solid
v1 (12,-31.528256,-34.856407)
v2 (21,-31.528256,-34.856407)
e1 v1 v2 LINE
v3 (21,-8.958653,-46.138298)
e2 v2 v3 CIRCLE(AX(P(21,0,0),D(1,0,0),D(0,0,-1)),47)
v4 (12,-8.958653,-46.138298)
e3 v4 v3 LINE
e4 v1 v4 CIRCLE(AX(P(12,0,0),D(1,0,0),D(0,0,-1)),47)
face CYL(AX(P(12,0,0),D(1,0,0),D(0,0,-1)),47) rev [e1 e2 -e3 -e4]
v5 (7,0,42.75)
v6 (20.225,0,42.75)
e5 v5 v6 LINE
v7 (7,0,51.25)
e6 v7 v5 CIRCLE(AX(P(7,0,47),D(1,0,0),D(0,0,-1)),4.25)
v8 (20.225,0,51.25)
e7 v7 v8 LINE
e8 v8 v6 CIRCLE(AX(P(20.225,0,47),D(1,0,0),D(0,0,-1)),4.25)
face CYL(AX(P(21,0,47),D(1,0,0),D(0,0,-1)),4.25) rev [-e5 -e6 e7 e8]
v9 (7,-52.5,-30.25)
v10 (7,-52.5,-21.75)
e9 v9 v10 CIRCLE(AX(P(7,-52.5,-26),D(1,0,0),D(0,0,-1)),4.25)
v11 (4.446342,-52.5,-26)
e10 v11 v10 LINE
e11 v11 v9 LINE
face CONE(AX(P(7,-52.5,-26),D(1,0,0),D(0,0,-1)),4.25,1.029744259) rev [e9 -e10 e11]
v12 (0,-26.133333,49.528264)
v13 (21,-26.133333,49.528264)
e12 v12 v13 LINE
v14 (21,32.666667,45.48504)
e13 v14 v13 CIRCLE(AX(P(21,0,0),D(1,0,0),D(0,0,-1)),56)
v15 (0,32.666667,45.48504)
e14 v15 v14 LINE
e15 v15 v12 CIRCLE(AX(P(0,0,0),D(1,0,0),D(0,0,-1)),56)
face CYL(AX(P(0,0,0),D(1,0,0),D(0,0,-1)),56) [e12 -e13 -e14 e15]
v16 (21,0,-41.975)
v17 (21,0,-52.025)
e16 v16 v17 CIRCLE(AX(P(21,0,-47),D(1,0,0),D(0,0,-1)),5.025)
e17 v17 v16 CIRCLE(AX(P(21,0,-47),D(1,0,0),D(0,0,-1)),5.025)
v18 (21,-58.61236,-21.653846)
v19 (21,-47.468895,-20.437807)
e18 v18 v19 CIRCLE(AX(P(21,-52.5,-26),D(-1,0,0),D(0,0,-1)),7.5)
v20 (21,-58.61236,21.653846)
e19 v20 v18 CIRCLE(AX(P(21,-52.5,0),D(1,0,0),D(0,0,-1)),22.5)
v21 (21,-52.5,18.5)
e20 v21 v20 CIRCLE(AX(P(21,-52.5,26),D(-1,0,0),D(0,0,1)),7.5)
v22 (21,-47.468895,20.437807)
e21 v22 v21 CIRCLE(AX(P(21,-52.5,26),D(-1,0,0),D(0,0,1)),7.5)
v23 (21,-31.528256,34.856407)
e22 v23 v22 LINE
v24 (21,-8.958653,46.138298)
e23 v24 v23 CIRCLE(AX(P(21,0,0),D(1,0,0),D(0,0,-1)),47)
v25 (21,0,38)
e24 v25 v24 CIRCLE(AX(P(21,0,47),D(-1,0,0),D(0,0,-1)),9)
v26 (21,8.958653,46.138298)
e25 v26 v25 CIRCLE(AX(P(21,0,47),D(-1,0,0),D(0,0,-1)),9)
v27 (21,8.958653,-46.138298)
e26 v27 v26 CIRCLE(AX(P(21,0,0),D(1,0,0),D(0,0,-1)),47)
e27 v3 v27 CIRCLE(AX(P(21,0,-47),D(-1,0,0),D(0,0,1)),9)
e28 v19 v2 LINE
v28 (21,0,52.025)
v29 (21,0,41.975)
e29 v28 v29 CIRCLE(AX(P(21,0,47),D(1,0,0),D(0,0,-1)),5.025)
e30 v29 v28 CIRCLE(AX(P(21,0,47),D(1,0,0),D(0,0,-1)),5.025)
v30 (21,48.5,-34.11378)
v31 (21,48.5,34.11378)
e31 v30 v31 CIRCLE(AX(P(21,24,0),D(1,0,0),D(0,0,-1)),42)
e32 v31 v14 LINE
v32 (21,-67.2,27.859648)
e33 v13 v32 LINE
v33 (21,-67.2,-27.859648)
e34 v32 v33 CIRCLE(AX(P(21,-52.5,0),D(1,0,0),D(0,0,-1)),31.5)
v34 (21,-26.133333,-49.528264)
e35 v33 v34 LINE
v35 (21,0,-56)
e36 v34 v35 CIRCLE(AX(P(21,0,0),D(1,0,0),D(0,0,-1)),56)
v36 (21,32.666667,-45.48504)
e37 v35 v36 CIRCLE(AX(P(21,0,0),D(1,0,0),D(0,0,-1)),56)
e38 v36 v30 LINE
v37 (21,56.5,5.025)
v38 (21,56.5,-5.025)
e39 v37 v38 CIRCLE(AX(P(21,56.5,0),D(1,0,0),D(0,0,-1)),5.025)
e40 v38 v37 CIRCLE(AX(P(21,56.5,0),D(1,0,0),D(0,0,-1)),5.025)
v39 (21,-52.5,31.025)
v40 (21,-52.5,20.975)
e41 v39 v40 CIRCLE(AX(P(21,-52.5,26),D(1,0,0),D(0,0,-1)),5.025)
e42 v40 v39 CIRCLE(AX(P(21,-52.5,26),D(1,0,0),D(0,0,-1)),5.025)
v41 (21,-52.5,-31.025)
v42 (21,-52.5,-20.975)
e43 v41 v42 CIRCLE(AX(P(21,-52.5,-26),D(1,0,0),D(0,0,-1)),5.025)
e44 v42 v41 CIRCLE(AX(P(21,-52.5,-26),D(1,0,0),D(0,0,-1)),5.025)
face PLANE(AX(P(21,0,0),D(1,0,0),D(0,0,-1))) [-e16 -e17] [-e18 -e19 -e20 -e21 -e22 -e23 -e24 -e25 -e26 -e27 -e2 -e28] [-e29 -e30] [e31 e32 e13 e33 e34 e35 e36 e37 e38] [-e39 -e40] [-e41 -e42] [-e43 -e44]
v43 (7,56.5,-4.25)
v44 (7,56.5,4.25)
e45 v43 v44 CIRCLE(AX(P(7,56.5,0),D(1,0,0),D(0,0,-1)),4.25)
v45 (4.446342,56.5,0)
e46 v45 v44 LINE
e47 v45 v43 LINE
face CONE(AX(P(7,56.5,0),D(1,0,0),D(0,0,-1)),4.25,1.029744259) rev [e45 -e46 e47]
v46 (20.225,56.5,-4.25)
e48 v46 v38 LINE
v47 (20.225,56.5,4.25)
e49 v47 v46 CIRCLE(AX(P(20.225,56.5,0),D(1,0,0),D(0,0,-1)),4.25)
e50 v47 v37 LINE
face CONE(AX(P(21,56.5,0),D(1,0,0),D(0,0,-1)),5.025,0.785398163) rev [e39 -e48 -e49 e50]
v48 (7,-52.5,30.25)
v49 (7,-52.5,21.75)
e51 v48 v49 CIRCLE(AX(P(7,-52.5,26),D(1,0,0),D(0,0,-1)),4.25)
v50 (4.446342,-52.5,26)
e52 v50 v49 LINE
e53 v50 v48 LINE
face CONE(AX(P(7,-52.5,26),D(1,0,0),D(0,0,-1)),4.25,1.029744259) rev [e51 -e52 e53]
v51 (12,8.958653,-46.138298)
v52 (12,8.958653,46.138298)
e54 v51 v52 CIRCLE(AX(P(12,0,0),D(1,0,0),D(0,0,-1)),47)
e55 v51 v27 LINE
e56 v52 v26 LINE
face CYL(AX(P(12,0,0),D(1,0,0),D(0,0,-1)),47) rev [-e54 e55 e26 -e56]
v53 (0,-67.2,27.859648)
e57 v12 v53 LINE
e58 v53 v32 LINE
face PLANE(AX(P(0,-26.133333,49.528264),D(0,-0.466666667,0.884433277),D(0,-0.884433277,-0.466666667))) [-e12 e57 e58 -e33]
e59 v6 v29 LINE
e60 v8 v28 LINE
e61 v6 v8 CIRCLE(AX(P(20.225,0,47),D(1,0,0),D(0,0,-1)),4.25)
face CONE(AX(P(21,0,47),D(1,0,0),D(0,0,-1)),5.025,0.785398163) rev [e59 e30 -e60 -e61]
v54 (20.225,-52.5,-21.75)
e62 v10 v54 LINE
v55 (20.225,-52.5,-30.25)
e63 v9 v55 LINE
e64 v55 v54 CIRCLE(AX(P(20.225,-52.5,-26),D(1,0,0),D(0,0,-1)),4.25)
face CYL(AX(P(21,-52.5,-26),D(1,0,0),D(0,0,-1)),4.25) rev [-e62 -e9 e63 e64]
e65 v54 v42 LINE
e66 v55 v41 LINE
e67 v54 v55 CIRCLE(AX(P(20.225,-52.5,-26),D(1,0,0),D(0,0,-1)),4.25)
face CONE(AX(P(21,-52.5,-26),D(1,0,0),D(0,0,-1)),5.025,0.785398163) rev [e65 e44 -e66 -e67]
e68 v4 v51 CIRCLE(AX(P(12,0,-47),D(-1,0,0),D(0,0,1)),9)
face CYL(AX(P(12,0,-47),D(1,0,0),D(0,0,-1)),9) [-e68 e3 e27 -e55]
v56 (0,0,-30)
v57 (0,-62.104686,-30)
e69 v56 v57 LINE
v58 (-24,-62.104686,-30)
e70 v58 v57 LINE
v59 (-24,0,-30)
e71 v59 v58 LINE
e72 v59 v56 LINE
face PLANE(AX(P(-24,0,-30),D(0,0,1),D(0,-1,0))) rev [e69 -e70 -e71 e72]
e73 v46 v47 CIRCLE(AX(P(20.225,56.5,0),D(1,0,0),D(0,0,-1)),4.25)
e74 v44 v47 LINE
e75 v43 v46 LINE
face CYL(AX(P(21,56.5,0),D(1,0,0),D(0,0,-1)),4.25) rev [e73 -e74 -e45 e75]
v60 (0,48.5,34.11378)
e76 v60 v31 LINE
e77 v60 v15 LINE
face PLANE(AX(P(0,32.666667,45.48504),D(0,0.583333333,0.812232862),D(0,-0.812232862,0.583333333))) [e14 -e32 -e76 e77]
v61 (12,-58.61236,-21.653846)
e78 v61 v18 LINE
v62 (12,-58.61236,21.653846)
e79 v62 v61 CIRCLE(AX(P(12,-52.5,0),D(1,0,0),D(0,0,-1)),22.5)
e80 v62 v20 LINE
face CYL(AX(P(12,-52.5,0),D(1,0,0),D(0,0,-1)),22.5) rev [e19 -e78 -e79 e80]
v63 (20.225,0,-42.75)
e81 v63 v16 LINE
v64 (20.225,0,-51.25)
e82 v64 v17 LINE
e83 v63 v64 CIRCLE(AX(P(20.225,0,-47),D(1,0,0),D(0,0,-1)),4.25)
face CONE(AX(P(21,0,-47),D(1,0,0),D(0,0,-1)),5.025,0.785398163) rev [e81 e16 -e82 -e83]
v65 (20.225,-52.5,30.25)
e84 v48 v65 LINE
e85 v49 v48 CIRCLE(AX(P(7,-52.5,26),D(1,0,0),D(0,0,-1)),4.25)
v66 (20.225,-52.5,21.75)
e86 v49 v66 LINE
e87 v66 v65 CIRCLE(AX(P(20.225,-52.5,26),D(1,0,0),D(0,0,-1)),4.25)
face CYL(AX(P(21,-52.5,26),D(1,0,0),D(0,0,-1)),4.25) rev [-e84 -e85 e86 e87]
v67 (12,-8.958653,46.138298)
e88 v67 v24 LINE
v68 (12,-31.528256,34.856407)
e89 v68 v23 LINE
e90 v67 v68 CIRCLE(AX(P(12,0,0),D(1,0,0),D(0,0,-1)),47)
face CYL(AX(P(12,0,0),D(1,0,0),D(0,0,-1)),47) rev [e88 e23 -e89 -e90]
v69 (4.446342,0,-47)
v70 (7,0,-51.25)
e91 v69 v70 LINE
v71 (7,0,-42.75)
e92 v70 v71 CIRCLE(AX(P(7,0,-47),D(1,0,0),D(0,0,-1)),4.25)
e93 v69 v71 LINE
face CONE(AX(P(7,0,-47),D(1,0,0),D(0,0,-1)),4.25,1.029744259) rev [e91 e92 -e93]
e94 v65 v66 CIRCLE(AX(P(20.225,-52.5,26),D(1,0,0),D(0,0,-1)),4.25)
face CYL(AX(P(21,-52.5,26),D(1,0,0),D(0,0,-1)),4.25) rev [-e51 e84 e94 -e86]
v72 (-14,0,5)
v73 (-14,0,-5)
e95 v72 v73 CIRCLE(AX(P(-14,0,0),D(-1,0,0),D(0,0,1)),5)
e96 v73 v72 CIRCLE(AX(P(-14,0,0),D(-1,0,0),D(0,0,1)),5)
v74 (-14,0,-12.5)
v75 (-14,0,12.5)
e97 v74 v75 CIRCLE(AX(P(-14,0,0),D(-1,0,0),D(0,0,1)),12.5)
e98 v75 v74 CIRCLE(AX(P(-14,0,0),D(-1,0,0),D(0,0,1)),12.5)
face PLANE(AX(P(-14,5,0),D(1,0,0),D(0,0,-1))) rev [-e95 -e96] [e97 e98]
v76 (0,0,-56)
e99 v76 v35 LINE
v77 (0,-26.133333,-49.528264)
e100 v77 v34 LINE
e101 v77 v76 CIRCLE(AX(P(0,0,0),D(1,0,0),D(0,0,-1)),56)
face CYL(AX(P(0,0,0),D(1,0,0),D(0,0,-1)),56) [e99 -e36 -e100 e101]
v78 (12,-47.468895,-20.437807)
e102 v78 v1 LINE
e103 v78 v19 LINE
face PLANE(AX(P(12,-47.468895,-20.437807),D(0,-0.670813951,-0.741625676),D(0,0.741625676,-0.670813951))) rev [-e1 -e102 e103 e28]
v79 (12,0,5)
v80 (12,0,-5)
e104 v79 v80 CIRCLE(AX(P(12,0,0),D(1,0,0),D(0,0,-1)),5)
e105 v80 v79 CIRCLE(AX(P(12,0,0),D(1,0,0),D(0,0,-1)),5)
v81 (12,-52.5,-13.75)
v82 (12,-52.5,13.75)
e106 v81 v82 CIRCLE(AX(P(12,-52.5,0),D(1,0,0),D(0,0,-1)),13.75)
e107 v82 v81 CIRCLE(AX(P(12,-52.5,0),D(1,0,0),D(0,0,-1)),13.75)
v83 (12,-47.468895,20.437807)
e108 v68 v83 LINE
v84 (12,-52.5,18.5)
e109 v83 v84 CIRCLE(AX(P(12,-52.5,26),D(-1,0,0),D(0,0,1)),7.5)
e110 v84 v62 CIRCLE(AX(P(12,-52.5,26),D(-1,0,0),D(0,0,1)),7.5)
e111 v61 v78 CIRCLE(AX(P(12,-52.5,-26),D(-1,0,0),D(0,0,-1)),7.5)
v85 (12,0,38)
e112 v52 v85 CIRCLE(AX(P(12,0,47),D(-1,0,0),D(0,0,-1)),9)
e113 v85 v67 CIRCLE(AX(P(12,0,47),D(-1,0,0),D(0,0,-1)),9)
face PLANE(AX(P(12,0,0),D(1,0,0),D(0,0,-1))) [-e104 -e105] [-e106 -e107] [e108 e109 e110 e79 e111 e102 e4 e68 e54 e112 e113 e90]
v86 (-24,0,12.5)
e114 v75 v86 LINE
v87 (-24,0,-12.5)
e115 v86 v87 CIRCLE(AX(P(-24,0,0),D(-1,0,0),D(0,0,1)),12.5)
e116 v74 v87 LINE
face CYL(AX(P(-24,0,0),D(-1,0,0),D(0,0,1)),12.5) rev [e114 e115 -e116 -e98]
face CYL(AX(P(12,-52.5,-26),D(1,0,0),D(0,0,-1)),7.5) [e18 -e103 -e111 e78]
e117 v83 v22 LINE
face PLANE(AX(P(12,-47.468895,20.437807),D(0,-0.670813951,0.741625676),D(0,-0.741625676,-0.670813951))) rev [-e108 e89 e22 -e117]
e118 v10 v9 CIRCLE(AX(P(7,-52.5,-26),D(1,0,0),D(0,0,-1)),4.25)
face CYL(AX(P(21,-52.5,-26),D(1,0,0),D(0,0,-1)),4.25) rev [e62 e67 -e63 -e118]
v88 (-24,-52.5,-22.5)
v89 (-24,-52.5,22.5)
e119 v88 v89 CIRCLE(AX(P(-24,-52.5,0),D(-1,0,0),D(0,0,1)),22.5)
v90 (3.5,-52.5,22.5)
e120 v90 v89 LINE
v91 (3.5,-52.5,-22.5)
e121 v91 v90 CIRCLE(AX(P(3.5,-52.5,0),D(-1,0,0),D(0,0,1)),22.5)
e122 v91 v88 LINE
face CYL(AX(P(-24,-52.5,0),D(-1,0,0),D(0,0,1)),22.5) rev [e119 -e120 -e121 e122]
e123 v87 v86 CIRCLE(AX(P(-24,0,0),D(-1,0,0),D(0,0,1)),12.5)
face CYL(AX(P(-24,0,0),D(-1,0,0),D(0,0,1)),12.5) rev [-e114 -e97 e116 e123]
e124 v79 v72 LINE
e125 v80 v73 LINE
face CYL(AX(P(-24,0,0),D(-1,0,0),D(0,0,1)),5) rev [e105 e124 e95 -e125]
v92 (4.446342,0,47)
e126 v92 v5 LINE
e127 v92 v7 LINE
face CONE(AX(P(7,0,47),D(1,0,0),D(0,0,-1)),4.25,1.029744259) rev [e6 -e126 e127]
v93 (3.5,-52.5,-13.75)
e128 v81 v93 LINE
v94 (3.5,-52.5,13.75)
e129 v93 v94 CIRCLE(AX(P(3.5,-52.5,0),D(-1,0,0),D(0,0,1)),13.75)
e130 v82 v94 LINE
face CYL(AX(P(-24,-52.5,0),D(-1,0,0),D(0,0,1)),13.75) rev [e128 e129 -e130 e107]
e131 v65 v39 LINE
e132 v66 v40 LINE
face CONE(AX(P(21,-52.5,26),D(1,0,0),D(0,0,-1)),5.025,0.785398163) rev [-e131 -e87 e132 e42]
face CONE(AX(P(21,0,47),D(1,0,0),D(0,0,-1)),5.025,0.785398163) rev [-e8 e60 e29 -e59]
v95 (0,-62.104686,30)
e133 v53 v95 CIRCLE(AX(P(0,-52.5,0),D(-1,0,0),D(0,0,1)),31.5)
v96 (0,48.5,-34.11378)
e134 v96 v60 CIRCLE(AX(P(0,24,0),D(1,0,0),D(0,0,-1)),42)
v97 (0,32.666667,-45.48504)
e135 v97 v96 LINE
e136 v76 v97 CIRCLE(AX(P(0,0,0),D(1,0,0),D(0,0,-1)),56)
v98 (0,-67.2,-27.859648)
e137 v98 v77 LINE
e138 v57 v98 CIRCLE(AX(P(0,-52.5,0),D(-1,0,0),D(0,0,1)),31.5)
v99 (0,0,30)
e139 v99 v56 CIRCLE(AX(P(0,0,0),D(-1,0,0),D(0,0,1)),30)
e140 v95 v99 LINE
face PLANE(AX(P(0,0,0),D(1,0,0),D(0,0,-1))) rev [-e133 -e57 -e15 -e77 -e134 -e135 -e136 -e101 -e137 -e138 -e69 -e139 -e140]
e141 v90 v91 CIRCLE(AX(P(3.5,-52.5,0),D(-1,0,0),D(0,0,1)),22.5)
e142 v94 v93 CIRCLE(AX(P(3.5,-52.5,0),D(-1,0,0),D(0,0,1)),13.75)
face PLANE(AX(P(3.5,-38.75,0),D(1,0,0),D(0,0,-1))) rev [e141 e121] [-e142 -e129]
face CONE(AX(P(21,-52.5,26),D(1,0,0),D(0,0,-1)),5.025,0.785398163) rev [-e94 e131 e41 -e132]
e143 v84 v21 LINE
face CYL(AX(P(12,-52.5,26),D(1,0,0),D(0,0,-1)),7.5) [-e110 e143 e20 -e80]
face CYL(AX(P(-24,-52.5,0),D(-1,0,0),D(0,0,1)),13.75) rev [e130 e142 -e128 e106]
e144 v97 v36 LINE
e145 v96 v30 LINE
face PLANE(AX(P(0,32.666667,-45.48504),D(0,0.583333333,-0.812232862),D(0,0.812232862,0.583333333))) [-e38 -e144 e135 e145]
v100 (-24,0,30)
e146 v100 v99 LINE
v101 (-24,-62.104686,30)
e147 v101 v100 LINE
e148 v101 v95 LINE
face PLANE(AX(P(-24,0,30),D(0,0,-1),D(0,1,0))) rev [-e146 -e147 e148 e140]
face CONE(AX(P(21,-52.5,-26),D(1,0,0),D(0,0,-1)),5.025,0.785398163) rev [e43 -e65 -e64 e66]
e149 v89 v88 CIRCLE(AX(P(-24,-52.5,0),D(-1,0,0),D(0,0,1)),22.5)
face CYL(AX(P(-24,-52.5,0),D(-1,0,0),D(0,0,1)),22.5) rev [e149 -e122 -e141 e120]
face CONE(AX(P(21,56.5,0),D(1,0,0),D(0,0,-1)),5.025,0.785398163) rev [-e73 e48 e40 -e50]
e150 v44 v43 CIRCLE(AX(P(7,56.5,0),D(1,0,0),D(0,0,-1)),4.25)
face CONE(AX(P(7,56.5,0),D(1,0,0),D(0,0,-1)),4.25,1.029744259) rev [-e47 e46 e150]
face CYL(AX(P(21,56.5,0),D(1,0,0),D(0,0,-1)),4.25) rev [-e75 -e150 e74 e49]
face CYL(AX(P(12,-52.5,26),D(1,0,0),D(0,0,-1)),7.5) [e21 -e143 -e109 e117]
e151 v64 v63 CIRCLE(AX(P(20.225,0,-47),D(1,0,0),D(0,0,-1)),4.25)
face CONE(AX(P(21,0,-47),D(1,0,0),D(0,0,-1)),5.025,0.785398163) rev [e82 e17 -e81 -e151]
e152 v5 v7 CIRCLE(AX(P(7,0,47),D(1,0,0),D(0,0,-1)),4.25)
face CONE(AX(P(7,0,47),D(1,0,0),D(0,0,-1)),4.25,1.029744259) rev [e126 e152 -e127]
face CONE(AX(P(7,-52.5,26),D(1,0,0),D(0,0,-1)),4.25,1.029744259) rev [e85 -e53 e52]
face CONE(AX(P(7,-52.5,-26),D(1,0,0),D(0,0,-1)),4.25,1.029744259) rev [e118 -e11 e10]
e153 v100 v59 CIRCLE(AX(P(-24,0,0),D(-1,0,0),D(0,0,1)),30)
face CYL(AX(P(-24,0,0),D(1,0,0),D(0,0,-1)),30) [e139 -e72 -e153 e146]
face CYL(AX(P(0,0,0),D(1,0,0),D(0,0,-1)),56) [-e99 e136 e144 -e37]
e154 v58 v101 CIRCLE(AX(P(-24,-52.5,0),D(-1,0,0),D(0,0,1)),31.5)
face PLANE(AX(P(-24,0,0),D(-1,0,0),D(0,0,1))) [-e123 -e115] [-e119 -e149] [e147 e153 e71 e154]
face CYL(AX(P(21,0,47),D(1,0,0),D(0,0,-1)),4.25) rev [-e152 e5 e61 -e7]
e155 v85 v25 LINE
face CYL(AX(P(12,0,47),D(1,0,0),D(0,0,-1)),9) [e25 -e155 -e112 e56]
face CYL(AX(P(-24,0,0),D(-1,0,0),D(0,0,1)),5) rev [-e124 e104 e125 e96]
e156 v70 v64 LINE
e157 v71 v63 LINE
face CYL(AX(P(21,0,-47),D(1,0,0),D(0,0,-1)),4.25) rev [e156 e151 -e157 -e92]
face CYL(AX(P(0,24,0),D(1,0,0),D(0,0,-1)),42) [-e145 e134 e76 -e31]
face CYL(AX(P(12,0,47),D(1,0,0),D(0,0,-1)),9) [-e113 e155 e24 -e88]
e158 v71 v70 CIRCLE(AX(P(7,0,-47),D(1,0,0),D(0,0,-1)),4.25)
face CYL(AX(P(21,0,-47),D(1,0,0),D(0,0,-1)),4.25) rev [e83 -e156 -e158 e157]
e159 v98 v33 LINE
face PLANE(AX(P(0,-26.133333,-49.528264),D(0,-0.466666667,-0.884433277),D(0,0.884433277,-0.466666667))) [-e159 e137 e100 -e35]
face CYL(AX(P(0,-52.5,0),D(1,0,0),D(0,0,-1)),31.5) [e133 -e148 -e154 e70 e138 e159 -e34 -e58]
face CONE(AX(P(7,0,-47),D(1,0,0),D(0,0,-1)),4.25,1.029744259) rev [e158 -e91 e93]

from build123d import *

# Parameters (mm, degrees)
PLATE_PROFILE_SKETCH_W             = 112
PLATE_PROFILE_SKETCH_H             = 150
COVER_PLATE_21MM_DEPTH             = 21
INNER_RECESS_SKETCH_OUTSIDE_W      = 151.674
INNER_RECESS_SKETCH_OUTSIDE_H      = 189.674
INNER_RECESS_CUT_DEPTH             = 21
BORE_BOSS_60_DEPTH                 = 24
FACE_RECESS_9MM_DEPTH              = 9
M10_TAPPED_HOLES_D                 = 8.5
M10_TAPPED_HOLES_DEPTH             = 14
M10_TAPPED_HOLES_CSINK_D           = 10.05
M10_TAPPED_HOLES_CSINK_ANGLE       = 90
M10_TAPPED_HOLES_TIP               = 2.553657631
COUNTERBORED_HOLE_10_D             = 10
COUNTERBORED_HOLE_10_DEPTH         = 100
COUNTERBORED_HOLE_10_CBORE_D       = 25
COUNTERBORED_HOLE_10_CBORE_DEPTH   = 10
COUNTERBORED_BORE_27_5_D           = 27.5
COUNTERBORED_BORE_27_5_DEPTH       = 100
COUNTERBORED_BORE_27_5_CBORE_D     = 45
COUNTERBORED_BORE_27_5_CBORE_DEPTH = 27.5


with BuildPart() as part:
    # Plate Profile Sketch → Cover Plate 21mm (new body)
    with BuildSketch(Plane(origin=(0, 0, 0), x_dir=(0, 0, -1), z_dir=(1, 0, 0))):
        with Locations((0, -9)):
            Rectangle(PLATE_PROFILE_SKETCH_W, PLATE_PROFILE_SKETCH_H)
    extrude(amount=COVER_PLATE_21MM_DEPTH)

    # Inner Recess Sketch outside → Inner Recess Cut (cut)
    with BuildSketch(Plane(origin=(21, 0, 0), x_dir=(0, 0, -1), z_dir=(1, 0, 0))):
        with Locations((0, -9)):
            Rectangle(INNER_RECESS_SKETCH_OUTSIDE_W, INNER_RECESS_SKETCH_OUTSIDE_H)
        with BuildLine():
            Line((-49.528263536, -26.133333333), (-27.859648239, -67.2))
            ThreePointArc((-27.859648239, -67.2), (0, -84), (27.859648239, -67.2))
            Line((27.859648239, -67.2), (49.528263536, -26.133333333))
            ThreePointArc((49.528263536, -26.133333333), (55.868076531, 3.841617458), (45.485040276, 32.666666667))
            Line((45.485040276, 32.666666667), (34.113780207, 48.5))
            ThreePointArc((34.113780207, 48.5), (0, 66), (-34.113780207, 48.5))
            Line((-34.113780207, 48.5), (-45.485040276, 32.666666667))
            ThreePointArc((-45.485040276, 32.666666667), (-55.868076531, 3.841617458), (-49.528263536, -26.133333333))
        make_face(mode=Mode.SUBTRACT)
    extrude(amount=-INNER_RECESS_CUT_DEPTH, mode=Mode.SUBTRACT)

    # Bore Boss Sketch → Bore Boss Ø60 (add)
    with BuildSketch(Plane.ZY):
        with BuildLine():
            Line((30, 0), (30, -62.104686356))
            ThreePointArc((30, -62.104686356), (0, -84), (-30, -62.104686356))
            Line((-30, -62.104686356), (-30, 0))
            ThreePointArc((-30, 0), (0, 30), (30, 0))
        make_face()
    extrude(amount=BORE_BOSS_60_DEPTH)

    # Face Recess Sketch → Face Recess 9mm (cut)
    with BuildSketch(Plane(origin=(21, 0, 0), x_dir=(0, 0, -1), z_dir=(1, 0, 0))):
        with BuildLine():
            Line((-20.437807431, -47.468895368), (-34.856406768, -31.528255696))
            ThreePointArc((-34.856406768, -31.528255696), (-42.040245988, -21.014702408), (-46.138297872, -8.958653328))
            ThreePointArc((-46.138297872, -8.958653328), (-38, 0), (-46.138297872, 8.958653328))
            ThreePointArc((-46.138297872, 8.958653328), (0, 47), (46.138297872, 8.958653328))
            ThreePointArc((46.138297872, 8.958653328), (38, 0), (46.138297872, -8.958653328))
            ThreePointArc((46.138297872, -8.958653328), (42.040245988, -21.014702408), (34.856406768, -31.528255696))
            Line((34.856406768, -31.528255696), (20.437807431, -47.468895368))
            ThreePointArc((20.437807431, -47.468895368), (18.544261668, -53.313612883), (21.653846154, -58.612360162))
            ThreePointArc((21.653846154, -58.612360162), (0, -75), (-21.653846154, -58.612360162))
            ThreePointArc((-21.653846154, -58.612360162), (-18.544261668, -53.313612883), (-20.437807431, -47.468895368))
        make_face()
    extrude(amount=-FACE_RECESS_9MM_DEPTH, mode=Mode.SUBTRACT)

    # M10 Tapped Holes
    with Locations(Plane(origin=(21, 0, 0), x_dir=(0, 0, -1), z_dir=(1, 0, 0))):
        with Locations((-47, 0), (47, 0), (26, -52.5), (-26, -52.5), (0, 56.5)):
            CounterSinkHole(M10_TAPPED_HOLES_D / 2, M10_TAPPED_HOLES_CSINK_D / 2, depth=M10_TAPPED_HOLES_DEPTH, counter_sink_angle=M10_TAPPED_HOLES_CSINK_ANGLE)
            with Locations((0, 0, -(M10_TAPPED_HOLES_DEPTH + M10_TAPPED_HOLES_TIP / 2))):  # 118° drill point
                Cone(0, M10_TAPPED_HOLES_D / 2, M10_TAPPED_HOLES_TIP, mode=Mode.SUBTRACT)

    # Counterbored Hole Ø10
    with Locations(Plane.ZY.offset(24)):
        with Locations((0, 0)):
            CounterBoreHole(COUNTERBORED_HOLE_10_D / 2, COUNTERBORED_HOLE_10_CBORE_D / 2, COUNTERBORED_HOLE_10_CBORE_DEPTH, depth=COUNTERBORED_HOLE_10_DEPTH)

    # Counterbored Bore Ø27.5
    with Locations(Plane.ZY.offset(24)):
        with Locations((0, -52.5)):
            CounterBoreHole(COUNTERBORED_BORE_27_5_D / 2, COUNTERBORED_BORE_27_5_CBORE_D / 2, COUNTERBORED_BORE_27_5_CBORE_DEPTH, depth=COUNTERBORED_BORE_27_5_DEPTH)


solid = part.part
